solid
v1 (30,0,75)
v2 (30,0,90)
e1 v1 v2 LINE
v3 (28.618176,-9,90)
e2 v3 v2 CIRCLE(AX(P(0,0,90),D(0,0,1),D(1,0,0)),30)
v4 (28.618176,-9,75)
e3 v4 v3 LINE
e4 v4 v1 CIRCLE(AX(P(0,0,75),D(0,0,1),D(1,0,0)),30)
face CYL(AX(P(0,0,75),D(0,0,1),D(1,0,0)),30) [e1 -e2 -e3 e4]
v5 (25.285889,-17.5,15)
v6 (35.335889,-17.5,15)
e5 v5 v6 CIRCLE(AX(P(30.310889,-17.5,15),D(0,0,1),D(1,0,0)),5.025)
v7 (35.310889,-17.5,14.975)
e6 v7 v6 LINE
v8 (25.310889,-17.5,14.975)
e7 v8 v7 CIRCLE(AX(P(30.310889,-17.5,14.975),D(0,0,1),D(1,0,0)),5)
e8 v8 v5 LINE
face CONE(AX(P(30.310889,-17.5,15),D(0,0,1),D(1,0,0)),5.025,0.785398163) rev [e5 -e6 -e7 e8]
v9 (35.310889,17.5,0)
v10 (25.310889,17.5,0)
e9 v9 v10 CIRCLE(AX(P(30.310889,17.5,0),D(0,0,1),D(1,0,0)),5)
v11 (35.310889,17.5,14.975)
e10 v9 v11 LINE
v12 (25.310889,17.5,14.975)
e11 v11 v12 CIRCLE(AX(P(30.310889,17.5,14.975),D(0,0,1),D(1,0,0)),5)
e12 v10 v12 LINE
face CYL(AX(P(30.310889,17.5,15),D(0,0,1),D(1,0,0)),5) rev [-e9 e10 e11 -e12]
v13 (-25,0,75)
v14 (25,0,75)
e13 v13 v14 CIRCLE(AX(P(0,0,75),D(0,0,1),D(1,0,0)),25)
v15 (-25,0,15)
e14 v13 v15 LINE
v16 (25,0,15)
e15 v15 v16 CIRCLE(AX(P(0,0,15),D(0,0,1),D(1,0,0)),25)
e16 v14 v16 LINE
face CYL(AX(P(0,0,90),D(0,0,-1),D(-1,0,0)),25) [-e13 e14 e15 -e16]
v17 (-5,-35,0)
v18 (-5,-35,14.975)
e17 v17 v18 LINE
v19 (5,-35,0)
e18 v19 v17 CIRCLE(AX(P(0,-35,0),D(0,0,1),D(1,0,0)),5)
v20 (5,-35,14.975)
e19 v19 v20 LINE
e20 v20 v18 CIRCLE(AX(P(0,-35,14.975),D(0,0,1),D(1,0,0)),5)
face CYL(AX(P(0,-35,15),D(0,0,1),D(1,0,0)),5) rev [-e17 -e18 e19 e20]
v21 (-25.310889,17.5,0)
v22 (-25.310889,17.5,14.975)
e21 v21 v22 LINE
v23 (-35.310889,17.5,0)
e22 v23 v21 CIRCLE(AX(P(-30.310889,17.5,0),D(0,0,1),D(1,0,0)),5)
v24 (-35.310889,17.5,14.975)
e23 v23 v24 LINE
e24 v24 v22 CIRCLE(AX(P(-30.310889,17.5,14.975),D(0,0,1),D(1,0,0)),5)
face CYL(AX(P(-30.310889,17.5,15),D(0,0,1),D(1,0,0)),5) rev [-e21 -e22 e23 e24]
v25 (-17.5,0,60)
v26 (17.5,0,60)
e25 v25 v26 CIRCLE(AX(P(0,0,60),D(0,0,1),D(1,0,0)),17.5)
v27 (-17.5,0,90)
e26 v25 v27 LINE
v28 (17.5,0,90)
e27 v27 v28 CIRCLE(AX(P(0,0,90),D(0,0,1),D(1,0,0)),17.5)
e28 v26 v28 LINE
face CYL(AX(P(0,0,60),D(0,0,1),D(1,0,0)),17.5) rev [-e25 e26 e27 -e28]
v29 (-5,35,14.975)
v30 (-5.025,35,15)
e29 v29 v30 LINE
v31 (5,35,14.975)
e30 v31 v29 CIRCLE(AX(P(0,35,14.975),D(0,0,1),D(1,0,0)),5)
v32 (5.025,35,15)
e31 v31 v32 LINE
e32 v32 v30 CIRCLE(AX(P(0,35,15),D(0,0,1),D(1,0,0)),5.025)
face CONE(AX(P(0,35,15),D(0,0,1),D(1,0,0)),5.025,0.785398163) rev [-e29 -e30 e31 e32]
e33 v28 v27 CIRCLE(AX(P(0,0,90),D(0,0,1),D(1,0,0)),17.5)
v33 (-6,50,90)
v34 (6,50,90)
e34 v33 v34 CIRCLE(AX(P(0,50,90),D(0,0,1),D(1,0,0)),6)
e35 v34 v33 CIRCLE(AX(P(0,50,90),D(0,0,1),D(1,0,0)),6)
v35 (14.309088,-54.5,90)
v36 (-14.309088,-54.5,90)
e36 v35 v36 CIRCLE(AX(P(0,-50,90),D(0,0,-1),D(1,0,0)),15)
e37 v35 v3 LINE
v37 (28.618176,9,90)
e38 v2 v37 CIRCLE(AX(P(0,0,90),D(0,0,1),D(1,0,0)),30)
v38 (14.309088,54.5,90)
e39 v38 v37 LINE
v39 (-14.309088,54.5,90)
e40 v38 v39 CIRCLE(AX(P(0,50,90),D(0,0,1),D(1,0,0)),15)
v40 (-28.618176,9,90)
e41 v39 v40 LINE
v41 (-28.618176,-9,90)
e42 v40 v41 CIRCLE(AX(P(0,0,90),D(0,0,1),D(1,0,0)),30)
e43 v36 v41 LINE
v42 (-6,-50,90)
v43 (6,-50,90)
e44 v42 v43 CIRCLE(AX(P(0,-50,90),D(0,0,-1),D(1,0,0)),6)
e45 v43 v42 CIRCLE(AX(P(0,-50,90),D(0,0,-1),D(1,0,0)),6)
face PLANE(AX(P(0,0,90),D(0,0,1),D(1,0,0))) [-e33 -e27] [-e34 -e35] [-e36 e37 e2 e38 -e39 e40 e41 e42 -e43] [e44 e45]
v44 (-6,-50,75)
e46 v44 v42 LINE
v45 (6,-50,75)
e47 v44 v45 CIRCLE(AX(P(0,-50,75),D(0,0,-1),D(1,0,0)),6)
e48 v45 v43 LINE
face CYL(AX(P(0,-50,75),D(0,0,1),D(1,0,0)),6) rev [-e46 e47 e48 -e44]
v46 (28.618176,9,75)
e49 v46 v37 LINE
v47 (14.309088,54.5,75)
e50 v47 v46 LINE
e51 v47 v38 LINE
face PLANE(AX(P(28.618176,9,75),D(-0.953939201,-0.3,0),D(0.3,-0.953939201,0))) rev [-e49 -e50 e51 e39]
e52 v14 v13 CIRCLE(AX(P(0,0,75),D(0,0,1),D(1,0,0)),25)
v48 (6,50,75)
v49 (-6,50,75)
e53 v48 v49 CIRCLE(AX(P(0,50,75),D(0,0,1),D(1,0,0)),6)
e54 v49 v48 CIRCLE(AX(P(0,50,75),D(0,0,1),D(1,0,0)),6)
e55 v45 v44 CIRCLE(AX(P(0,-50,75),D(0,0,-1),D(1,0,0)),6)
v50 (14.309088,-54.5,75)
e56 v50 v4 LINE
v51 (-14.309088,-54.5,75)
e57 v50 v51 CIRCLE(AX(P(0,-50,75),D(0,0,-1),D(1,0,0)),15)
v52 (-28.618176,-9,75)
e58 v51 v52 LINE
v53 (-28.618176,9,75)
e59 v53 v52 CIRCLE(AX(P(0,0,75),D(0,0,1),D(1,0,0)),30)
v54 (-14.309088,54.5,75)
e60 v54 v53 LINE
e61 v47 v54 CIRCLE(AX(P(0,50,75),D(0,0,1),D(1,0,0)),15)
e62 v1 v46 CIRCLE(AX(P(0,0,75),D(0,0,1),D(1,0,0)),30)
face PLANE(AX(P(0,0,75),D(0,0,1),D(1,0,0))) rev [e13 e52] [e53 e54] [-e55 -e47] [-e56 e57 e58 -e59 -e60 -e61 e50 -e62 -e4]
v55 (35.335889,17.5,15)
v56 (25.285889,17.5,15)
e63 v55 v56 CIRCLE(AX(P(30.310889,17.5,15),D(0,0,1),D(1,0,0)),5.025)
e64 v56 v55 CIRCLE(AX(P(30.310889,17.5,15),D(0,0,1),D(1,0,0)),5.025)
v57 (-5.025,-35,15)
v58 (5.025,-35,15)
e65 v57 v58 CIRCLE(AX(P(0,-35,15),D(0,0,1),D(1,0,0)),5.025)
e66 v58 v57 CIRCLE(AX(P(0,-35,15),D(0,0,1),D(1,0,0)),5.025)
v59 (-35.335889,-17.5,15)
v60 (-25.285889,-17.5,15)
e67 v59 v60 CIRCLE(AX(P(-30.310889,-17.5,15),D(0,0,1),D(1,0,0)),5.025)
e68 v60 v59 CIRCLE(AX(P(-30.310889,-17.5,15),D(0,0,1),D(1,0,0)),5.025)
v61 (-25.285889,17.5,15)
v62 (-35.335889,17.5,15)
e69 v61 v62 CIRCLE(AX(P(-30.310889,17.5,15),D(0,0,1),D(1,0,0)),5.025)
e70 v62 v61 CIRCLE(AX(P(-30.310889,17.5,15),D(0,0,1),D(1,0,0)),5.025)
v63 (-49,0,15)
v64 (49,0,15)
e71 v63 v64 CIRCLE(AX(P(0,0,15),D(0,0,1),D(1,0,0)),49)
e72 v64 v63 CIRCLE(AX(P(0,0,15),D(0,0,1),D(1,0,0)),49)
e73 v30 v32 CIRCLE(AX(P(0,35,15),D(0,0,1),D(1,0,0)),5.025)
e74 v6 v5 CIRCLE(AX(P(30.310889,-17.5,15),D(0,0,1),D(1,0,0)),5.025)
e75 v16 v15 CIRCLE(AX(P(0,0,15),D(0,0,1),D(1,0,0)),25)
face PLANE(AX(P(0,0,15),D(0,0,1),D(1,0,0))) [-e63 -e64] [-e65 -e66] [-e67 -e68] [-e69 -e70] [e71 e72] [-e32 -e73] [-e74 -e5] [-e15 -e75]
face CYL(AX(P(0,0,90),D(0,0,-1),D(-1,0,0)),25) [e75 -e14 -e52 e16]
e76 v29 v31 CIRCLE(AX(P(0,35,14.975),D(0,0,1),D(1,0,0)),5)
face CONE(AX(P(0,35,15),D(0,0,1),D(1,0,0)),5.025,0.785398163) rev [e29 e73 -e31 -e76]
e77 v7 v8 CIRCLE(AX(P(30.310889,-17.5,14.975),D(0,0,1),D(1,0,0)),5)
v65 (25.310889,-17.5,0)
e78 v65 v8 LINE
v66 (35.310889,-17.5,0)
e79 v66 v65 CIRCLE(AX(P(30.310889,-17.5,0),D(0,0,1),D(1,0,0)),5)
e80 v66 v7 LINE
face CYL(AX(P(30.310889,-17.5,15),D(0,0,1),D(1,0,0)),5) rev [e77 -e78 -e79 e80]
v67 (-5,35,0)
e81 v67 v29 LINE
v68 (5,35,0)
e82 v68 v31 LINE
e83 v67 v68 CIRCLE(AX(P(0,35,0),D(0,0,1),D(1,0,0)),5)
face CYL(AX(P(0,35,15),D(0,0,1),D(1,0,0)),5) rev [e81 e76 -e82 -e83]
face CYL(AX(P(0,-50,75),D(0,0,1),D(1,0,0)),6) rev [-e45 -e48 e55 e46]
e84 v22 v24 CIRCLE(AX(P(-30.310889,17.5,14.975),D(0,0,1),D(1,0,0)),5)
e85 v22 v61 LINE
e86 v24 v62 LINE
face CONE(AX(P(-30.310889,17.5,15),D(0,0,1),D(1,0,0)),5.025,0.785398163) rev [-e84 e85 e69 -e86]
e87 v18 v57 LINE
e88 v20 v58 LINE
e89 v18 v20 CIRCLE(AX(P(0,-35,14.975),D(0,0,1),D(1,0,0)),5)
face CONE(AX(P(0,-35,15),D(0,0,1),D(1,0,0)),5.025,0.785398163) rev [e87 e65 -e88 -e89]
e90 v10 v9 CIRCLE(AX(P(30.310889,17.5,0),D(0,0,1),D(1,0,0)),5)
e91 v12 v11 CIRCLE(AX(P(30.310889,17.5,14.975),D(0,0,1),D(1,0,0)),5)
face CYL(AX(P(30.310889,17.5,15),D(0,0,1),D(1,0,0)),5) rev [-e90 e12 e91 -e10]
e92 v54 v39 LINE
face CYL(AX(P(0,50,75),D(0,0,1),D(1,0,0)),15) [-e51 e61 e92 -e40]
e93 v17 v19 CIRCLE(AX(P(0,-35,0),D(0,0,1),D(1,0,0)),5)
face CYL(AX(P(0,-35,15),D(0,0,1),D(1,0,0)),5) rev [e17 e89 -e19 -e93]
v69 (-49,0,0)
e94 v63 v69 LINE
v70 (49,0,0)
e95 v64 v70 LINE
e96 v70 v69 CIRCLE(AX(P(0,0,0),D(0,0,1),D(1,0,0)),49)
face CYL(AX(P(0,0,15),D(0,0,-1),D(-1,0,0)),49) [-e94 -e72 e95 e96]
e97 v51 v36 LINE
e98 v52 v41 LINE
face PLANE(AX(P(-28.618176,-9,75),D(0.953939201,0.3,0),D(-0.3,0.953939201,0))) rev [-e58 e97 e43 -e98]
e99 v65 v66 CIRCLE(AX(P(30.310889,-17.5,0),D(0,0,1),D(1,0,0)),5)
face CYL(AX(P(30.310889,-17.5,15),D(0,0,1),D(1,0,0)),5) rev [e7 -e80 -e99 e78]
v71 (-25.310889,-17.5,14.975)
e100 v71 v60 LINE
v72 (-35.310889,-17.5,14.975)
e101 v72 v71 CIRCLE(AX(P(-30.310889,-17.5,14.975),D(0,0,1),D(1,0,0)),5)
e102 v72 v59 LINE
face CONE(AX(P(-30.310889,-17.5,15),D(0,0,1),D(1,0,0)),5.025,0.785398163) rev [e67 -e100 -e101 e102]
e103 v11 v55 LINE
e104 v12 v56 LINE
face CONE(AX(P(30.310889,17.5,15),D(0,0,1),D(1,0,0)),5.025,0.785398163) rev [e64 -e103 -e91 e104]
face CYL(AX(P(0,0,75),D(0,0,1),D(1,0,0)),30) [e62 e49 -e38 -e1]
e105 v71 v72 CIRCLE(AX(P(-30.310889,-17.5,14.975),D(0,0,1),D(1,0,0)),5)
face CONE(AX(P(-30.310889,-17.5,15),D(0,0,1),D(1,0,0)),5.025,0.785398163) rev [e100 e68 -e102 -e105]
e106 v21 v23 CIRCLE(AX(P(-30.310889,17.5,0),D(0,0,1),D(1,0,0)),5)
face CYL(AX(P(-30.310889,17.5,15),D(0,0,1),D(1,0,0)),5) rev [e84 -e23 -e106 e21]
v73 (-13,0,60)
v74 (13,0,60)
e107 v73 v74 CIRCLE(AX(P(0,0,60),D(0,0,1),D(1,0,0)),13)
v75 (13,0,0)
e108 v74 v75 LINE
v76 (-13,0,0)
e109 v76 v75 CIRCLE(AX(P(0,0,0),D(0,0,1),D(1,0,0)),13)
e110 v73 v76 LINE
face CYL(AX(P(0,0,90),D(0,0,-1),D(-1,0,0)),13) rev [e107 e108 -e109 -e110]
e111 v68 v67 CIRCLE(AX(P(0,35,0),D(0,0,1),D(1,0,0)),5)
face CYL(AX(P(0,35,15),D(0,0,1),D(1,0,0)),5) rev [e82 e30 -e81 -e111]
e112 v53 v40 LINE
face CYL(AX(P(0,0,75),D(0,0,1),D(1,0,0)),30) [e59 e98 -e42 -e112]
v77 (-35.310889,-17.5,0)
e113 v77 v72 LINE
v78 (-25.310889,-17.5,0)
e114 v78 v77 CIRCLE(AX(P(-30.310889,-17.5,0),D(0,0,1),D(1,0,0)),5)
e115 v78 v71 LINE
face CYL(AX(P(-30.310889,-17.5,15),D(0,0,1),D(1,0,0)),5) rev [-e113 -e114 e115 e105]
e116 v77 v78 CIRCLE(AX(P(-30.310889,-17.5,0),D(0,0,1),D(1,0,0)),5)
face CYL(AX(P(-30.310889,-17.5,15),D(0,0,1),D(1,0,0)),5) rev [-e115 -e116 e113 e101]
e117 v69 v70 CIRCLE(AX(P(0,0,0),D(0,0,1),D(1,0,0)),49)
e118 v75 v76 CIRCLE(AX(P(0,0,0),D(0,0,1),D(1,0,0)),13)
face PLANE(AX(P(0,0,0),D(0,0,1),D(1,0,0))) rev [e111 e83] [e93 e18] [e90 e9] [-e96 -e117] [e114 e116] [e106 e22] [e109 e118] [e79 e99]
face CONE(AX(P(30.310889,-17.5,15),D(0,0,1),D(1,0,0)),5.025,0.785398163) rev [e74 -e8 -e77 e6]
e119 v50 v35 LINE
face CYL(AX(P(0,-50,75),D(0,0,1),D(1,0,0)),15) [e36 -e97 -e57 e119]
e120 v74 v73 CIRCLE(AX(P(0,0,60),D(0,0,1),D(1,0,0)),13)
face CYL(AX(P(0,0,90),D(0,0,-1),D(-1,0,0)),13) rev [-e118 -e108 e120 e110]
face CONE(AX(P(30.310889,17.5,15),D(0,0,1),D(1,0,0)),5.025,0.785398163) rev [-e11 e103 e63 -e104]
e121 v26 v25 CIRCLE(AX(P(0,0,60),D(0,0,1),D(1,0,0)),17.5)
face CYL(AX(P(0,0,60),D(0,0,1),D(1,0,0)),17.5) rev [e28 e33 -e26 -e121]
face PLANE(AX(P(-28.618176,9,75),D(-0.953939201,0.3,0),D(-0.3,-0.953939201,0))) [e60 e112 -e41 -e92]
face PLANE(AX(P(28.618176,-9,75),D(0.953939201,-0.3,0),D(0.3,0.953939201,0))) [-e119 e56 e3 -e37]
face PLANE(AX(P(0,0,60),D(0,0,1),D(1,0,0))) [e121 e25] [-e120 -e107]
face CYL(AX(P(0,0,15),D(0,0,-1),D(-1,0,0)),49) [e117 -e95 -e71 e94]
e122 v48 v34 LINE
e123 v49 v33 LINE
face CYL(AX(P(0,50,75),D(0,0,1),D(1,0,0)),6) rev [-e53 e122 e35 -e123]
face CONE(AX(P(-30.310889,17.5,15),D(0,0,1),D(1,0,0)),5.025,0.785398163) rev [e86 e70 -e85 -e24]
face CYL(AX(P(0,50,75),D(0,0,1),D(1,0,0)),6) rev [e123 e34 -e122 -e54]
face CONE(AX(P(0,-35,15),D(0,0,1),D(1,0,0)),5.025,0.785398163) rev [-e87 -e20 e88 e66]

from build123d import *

# Parameters (mm, degrees)
FLANGE_AND_TUBE_PROFILE_SKETCH_R   = 49
FLANGE_AND_TUBE_PROFILE_SKETCH_R_2 = 25
ROUND_FLANGE_98_DEPTH              = 15
SKETCH1_3_R                        = 25
SKETCH1_3_R_2                      = 13
TUBE_BODY_50_DEPTH                 = 90
OVAL_START                         = -15
OVAL_FLANGE_PROFILE_SKETCH_R       = 6
OVAL_FLANGE_PROFILE_SKETCH_R_2     = 25
OVAL_MOUNTING_FLANGE_DEPTH         = 15
SKETCH2_3_R                        = 17.5
OVAL_FLANGE_BORE_CUT_DEPTH         = 30
FLANGE_HOLES_6X_10_D               = 10
FLANGE_HOLES_6X_10_DEPTH           = 15
FLANGE_HOLES_6X_10_CSINK_D         = 10.05
FLANGE_HOLES_6X_10_CSINK_ANGLE     = 90


with BuildPart() as part:
    # Flange and Tube Profile Sketch → Round Flange _98 (new body)
    with BuildSketch(Plane.XY):
        Circle(FLANGE_AND_TUBE_PROFILE_SKETCH_R)
        Circle(FLANGE_AND_TUBE_PROFILE_SKETCH_R_2, mode=Mode.SUBTRACT)
    extrude(amount=ROUND_FLANGE_98_DEPTH)

    # Sketch1_3 → Tube Body _50 (add)
    with BuildSketch(Plane.XY):
        with Locations(Location((0, 0, 0), (0, 0, 180))):
            Circle(SKETCH1_3_R)
        with Locations(Location((0, 0, 0), (0, 0, 180))):
            Circle(SKETCH1_3_R_2, mode=Mode.SUBTRACT)
    extrude(amount=TUBE_BODY_50_DEPTH)

    # Oval Flange Profile Sketch → Oval Mounting Flange (add)
    with BuildSketch(Plane.XY.offset(90).offset(OVAL_START)):
        with BuildLine():
            Line((14.309088021, -54.5), (28.618176043, -9))
            ThreePointArc((28.618176043, -9), (30, 0), (28.618176043, 9))
            Line((28.618176043, 9), (14.309088021, 54.5))
            ThreePointArc((14.309088021, 54.5), (0, 65), (-14.309088021, 54.5))
            Line((-14.309088021, 54.5), (-28.618176043, 9))
            ThreePointArc((-28.618176043, 9), (-30, 0), (-28.618176043, -9))
            Line((-28.618176043, -9), (-14.309088021, -54.5))
            ThreePointArc((-14.309088021, -54.5), (0, -65), (14.309088021, -54.5))
        make_face()
        with Locations((0, -50)):
            Circle(OVAL_FLANGE_PROFILE_SKETCH_R, mode=Mode.SUBTRACT)
        with Locations((0, 50)):
            Circle(OVAL_FLANGE_PROFILE_SKETCH_R, mode=Mode.SUBTRACT)
        with Locations(Location((0, 0, 0), (0, 0, 180))):
            Circle(OVAL_FLANGE_PROFILE_SKETCH_R_2, mode=Mode.SUBTRACT)
    extrude(amount=OVAL_MOUNTING_FLANGE_DEPTH)

    # Sketch2_3 → Oval Flange Bore Cut (cut)
    with BuildSketch(Plane.XY.offset(90)):
        Circle(SKETCH2_3_R)
    extrude(amount=-OVAL_FLANGE_BORE_CUT_DEPTH, mode=Mode.SUBTRACT)

    # Flange Holes 6x_10
    with Locations(Plane.XY.offset(15)):
        with Locations((-30.310889132, 17.5), (0, 35), (30.310889132, 17.5), (30.310889132, -17.5), (0, -35), (-30.310889132, -17.5)):
            CounterSinkHole(FLANGE_HOLES_6X_10_D / 2, FLANGE_HOLES_6X_10_CSINK_D / 2, depth=FLANGE_HOLES_6X_10_DEPTH, counter_sink_angle=FLANGE_HOLES_6X_10_CSINK_ANGLE)


solid = part.part
